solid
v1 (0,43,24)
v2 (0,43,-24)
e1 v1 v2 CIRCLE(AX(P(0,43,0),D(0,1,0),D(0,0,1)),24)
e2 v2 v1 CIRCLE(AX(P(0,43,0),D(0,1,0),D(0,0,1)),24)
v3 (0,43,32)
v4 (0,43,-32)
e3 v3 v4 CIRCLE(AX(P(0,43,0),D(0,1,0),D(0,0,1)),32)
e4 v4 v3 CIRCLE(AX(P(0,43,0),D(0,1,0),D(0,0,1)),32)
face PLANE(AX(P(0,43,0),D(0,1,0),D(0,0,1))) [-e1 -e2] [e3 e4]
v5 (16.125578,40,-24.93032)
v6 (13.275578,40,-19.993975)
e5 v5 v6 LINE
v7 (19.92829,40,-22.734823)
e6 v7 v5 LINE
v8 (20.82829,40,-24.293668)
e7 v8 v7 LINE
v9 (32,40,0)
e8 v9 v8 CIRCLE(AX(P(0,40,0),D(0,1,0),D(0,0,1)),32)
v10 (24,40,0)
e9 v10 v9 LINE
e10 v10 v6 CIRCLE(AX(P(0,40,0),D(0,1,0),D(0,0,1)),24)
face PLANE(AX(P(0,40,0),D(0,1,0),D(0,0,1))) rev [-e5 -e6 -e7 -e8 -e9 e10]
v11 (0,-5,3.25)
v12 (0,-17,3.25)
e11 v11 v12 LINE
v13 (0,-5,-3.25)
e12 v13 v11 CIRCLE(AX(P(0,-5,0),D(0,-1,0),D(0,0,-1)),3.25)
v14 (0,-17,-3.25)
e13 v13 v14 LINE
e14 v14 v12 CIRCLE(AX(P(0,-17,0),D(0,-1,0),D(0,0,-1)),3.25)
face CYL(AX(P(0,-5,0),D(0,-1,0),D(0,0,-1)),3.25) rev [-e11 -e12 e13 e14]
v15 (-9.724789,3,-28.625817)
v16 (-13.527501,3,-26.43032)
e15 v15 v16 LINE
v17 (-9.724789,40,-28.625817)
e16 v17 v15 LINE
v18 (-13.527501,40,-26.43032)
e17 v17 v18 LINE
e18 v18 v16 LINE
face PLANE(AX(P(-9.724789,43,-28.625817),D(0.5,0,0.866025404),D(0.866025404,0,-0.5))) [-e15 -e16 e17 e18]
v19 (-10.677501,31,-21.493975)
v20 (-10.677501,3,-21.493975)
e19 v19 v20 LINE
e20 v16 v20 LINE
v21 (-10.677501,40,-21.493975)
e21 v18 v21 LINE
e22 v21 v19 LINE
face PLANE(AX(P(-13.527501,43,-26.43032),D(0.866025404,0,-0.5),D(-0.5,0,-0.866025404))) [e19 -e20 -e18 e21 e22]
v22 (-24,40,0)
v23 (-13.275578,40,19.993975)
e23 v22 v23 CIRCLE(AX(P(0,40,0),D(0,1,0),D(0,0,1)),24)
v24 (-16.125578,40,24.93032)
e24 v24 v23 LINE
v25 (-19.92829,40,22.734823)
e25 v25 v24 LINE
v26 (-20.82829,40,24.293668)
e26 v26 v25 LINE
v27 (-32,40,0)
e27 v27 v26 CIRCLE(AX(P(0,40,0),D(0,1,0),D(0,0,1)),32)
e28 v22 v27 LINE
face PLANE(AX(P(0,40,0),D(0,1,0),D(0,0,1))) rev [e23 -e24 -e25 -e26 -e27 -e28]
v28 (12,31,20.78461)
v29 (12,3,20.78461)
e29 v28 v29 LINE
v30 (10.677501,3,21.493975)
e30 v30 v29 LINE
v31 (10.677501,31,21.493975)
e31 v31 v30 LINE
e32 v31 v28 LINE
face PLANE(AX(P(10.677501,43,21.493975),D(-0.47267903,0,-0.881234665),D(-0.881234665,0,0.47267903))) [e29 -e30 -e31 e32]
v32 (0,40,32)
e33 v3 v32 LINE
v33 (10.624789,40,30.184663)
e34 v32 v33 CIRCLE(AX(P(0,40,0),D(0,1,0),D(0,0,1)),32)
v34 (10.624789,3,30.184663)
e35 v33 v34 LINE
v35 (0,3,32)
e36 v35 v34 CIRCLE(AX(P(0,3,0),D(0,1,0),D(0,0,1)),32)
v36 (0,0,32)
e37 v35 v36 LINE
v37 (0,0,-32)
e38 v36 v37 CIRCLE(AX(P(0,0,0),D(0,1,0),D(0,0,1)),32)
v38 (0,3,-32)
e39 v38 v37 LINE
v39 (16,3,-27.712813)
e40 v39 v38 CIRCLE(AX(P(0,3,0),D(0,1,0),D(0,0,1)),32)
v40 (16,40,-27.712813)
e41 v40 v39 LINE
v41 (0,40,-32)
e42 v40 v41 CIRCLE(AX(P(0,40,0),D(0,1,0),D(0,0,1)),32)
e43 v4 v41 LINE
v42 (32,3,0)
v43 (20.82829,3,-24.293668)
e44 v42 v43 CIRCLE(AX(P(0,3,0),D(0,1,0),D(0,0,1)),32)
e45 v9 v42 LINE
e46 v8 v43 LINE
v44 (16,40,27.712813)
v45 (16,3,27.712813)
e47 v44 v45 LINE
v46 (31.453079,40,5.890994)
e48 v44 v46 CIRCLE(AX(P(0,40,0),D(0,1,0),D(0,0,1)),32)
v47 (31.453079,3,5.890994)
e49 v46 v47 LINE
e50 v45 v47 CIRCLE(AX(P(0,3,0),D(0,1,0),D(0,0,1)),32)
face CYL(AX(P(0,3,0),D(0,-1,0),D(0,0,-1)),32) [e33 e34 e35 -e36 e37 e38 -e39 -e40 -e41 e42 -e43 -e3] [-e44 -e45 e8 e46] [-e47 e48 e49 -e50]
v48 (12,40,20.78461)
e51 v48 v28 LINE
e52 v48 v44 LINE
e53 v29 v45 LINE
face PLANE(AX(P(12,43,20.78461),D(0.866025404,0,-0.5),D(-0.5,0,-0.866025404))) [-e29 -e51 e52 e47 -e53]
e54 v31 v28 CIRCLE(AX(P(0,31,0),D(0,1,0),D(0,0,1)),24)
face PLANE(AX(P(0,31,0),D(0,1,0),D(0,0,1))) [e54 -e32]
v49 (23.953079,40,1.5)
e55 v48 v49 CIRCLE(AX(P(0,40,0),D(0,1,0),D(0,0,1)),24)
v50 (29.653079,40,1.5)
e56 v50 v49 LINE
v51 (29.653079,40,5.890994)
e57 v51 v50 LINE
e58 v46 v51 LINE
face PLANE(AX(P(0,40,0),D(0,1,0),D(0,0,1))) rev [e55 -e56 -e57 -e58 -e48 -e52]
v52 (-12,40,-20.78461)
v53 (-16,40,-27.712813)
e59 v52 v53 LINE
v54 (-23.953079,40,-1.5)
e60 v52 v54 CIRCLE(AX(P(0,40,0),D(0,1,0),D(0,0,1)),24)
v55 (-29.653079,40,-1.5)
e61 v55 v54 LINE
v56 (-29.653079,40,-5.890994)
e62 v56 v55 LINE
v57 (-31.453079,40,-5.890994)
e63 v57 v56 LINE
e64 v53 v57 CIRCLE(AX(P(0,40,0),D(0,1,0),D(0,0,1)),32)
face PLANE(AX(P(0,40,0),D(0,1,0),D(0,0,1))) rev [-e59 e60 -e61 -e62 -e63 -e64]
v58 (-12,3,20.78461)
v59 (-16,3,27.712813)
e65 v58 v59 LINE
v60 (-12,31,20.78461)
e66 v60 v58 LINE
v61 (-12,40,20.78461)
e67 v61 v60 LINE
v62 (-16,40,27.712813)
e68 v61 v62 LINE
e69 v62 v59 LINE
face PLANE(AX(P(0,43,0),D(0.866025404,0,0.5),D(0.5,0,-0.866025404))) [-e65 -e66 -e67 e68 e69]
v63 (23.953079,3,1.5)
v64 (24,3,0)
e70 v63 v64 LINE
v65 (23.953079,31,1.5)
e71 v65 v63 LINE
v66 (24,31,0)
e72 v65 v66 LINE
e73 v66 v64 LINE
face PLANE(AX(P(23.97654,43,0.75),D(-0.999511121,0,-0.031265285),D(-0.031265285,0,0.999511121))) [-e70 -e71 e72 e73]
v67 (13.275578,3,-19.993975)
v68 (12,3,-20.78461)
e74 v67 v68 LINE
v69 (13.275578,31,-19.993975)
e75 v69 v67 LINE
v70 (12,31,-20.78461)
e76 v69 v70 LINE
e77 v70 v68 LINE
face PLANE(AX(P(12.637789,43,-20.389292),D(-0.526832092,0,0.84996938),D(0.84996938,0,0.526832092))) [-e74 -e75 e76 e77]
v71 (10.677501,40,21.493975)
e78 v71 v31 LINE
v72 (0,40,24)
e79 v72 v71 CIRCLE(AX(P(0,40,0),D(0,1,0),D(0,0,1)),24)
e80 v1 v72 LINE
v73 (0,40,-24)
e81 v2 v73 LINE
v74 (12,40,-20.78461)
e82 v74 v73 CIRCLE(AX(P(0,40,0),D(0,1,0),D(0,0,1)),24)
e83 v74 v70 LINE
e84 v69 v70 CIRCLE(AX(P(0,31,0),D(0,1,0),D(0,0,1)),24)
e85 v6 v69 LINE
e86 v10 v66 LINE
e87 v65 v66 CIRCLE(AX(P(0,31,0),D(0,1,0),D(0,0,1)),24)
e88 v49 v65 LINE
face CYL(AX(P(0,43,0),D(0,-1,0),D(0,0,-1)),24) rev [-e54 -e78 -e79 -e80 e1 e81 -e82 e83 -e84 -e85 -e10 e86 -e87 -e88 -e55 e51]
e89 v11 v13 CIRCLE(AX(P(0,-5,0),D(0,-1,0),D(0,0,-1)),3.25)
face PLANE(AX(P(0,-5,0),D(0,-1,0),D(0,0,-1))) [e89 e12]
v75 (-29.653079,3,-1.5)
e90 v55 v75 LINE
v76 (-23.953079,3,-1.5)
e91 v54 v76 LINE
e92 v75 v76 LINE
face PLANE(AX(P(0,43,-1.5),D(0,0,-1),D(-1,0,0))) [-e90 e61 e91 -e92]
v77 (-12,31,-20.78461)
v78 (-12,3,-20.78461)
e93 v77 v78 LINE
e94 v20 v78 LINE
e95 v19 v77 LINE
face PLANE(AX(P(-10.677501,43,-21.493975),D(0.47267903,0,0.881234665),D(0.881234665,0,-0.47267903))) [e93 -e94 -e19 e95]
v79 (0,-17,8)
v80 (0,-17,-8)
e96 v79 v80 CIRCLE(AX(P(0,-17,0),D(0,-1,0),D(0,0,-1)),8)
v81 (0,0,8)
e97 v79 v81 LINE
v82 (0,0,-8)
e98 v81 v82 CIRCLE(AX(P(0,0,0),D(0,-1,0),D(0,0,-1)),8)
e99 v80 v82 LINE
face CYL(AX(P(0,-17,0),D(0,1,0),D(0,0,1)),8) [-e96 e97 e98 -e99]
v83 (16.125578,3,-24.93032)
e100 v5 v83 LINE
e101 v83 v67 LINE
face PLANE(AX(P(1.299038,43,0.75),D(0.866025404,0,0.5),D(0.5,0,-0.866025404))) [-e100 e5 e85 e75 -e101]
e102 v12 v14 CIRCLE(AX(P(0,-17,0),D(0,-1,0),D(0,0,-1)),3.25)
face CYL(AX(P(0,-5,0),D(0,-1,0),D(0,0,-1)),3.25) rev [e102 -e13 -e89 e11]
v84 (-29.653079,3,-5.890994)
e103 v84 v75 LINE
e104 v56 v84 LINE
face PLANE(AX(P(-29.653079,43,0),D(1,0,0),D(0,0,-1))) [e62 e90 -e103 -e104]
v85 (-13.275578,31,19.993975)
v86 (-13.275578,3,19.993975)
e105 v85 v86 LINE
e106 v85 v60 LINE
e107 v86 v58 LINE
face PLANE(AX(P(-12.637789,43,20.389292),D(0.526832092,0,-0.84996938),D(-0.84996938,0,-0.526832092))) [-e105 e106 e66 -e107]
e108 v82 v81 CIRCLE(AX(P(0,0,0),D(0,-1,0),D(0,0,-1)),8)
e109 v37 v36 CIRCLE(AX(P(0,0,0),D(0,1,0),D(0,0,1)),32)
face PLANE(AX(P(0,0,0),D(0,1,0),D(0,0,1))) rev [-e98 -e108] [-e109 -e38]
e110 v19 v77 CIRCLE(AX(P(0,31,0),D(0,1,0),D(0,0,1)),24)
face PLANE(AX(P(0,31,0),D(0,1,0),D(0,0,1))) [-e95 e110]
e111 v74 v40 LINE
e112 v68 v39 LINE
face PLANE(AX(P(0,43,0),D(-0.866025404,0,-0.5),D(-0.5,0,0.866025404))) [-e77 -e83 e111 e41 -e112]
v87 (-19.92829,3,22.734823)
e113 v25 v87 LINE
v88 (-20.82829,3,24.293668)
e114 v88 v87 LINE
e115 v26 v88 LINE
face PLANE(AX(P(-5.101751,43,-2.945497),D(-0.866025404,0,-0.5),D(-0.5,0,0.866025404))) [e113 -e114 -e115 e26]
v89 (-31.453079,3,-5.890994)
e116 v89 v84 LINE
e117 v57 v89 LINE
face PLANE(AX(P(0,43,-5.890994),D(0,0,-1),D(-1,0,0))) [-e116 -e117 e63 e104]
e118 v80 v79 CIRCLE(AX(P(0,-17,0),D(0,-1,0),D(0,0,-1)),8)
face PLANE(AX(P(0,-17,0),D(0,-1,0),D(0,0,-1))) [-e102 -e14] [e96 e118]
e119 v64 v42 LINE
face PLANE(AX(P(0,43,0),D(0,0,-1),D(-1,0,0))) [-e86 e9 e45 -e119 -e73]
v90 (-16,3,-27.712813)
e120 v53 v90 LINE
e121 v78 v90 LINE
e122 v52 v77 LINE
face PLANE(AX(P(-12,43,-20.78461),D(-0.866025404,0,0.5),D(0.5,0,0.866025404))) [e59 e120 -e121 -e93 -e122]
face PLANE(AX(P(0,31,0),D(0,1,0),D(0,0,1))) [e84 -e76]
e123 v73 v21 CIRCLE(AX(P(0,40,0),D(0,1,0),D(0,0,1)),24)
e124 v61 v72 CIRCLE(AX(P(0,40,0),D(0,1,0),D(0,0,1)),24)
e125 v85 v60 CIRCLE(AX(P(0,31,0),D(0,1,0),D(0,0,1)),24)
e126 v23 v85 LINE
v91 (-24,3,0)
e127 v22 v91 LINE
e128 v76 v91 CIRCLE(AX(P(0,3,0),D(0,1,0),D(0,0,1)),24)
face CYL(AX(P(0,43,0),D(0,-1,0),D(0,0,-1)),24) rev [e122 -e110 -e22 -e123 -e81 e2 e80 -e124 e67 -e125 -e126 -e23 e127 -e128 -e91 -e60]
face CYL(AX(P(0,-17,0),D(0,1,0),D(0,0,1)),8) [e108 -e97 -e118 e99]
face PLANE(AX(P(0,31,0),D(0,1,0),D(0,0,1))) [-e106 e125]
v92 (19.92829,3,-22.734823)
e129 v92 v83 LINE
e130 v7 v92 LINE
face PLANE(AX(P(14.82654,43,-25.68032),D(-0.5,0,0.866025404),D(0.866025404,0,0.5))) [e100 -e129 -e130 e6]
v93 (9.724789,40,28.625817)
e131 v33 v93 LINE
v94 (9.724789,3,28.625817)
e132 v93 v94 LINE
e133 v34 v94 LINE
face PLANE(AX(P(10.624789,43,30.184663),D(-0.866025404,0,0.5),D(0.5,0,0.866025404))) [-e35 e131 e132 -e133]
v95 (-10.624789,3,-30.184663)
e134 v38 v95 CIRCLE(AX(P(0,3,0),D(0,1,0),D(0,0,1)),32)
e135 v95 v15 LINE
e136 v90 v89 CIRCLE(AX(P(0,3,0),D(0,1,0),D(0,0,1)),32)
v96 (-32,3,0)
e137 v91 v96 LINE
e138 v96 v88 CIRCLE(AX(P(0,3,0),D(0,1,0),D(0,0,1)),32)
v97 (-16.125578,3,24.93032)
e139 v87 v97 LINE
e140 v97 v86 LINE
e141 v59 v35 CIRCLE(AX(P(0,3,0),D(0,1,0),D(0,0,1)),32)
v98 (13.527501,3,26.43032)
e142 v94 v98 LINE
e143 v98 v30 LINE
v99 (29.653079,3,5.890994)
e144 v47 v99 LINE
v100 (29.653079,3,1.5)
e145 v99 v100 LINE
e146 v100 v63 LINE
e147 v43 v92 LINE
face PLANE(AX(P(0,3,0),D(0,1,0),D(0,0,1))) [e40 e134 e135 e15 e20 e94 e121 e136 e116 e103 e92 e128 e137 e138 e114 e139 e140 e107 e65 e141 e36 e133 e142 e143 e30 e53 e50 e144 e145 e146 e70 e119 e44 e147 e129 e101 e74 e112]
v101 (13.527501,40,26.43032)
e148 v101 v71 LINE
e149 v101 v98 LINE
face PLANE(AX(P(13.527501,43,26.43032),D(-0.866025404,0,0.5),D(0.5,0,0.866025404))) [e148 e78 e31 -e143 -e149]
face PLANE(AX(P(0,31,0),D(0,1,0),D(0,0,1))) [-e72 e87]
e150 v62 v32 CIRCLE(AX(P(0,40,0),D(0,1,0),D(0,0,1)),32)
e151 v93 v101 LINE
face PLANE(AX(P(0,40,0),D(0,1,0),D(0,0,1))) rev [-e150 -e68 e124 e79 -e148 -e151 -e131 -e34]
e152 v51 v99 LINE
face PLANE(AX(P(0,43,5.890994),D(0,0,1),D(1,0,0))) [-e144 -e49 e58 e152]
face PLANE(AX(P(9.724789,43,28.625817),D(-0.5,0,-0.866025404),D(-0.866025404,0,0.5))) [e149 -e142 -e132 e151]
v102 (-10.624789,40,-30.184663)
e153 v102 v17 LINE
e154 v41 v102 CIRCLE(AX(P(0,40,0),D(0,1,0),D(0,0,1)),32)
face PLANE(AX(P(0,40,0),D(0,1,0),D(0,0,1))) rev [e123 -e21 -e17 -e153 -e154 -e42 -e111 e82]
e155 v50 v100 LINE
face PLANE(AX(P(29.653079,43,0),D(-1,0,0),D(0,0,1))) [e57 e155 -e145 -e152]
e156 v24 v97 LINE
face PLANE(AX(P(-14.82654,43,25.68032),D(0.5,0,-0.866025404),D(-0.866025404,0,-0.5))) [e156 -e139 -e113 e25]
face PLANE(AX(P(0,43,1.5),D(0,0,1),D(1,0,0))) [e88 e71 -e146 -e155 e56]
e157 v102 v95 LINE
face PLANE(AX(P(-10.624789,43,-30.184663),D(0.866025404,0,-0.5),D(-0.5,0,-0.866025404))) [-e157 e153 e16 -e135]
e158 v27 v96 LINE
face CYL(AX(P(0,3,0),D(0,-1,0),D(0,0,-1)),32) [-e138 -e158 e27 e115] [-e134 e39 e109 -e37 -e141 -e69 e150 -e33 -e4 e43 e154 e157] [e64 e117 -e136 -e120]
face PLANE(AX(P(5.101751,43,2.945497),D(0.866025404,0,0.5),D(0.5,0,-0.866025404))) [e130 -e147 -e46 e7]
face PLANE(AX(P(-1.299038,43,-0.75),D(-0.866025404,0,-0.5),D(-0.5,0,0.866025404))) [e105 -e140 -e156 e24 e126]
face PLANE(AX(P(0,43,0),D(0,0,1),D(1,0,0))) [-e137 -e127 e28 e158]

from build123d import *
from build123d.topology import SkipClean

# Parameters (mm, degrees)
BASE_DISC_SKETCH_R    = 32
BASE_DISC_64_DEPTH    = 3
CAGE_POSTS_6X_DEPTH   = 40
TOP_START             = -3
TOP_RING_SKETCH_R     = 32
TOP_RING_DEPTH        = 3
HUB_SKETCH_R          = 8
HUB_16_DEPTH          = 17
HUB_BORE_SKETCH_R     = 3.25
HUB_BORE_6_5_DEPTH    = 12
INNER_START           = -12
INNER_RECESS_SKETCH_R = 24
INNER_RECESS_48_DEPTH = 12


with BuildPart() as part:
    # Base Disc Sketch → Base Disc Ø64 (new body)
    with BuildSketch(Plane(origin=(0, 0, 0), x_dir=(1, 0, 0), z_dir=(0, 1, 0))):
        with Locations(Location((0, 0, 0), (0, 0, 270))):
            Circle(BASE_DISC_SKETCH_R)
    extrude(amount=BASE_DISC_64_DEPTH)

    # Cage Posts Sketch → Cage Posts 6x (add)
    with SkipClean():  # the faces are left unmerged after this step: merging them gives an invalid solid
        with BuildSketch(Plane(origin=(0, 3, 0), x_dir=(1, 0, 0), z_dir=(0, 1, 0))):
            with BuildLine():
                Line((-19.928290222, -22.734822717), (-20.828290222, -24.293668443))
                ThreePointArc((-20.828290222, -24.293668443), (-18.493333323, -26.115065051), (-16, -27.712812921))
                Line((-16, -27.712812921), (-12, -20.784609691))
                Line((-12, -20.784609691), (-13.275577673, -19.993975029))
                Line((-13.275577673, -19.993975029), (-16.125577673, -24.93031983))
                Line((-16.125577673, -24.93031983), (-19.928290222, -22.734822717))
            make_face()
            with BuildLine():
                Line((29.653079134, -5.890994228), (31.453079134, -5.890994228))
                ThreePointArc((31.453079134, -5.890994228), (31.862976417, -2.958163933), (32, 0))
                Line((32, 0), (24, 0))
                Line((24, 0), (23.953079134, -1.5))
                Line((23.953079134, -1.5), (29.653079134, -1.5))
                Line((29.653079134, -1.5), (29.653079134, -5.890994228))
            make_face()
            with BuildLine():
                ThreePointArc((20.828290222, 24.293668443), (18.493333323, 26.115065051), (16, 27.712812921))
                Line((16, 27.712812921), (12, 20.784609691))
                Line((12, 20.784609691), (13.275577673, 19.993975029))
                Line((13.275577673, 19.993975029), (16.125577673, 24.93031983))
                Line((16.125577673, 24.93031983), (19.928290222, 22.734822717))
                Line((19.928290222, 22.734822717), (20.828290222, 24.293668443))
            make_face()
            with BuildLine():
                Line((-32, 0), (-24, 0))
                ThreePointArc((-24, 0), (-23.988266915, 0.750366838), (-23.953079134, 1.5))
                Line((-23.953079134, 1.5), (-29.653079134, 1.5))
                Line((-29.653079134, 1.5), (-29.653079134, 5.890994228))
                Line((-29.653079134, 5.890994228), (-31.453079134, 5.890994228))
                ThreePointArc((-31.453079134, 5.890994228), (-31.862976417, 2.958163933), (-32, 0))
            make_face()
            with BuildLine():
                Line((9.724788912, -28.625816944), (13.527501461, -26.43031983))
                Line((13.527501461, -26.43031983), (10.677501461, -21.493975029))
                Line((10.677501461, -21.493975029), (12, -20.784609691))
                Line((12, -20.784609691), (16, -27.712812921))
                ThreePointArc((16, -27.712812921), (13.369643094, -29.073228984), (10.624788912, -30.184662671))
                Line((10.624788912, -30.184662671), (9.724788912, -28.625816944))
            make_face()
            with BuildLine():
                ThreePointArc((-16, 27.712812921), (-13.369643094, 29.073228984), (-10.624788912, 30.184662671))
                Line((-10.624788912, 30.184662671), (-9.724788912, 28.625816944))
                Line((-9.724788912, 28.625816944), (-13.527501461, 26.43031983))
                Line((-13.527501461, 26.43031983), (-10.677501461, 21.493975029))
                Line((-10.677501461, 21.493975029), (-12, 20.784609691))
                Line((-12, 20.784609691), (-16, 27.712812921))
            make_face()
        extrude(amount=CAGE_POSTS_6X_DEPTH)

    # Top Ring Sketch → Top Ring (add)
    with SkipClean():  # the faces are left unmerged after this step: merging them gives an invalid solid
        with BuildSketch(Plane(origin=(0, 43, 0), x_dir=(1, 0, 0), z_dir=(0, 1, 0)).offset(TOP_START)):
            with Locations(Location((0, 0, 0), (0, 0, 270))):
                Circle(TOP_RING_SKETCH_R)
        extrude(amount=TOP_RING_DEPTH)

    # Hub Sketch → Hub Ø16 (add)
    with SkipClean():  # the faces are left unmerged after this step: merging them gives an invalid solid
        with BuildSketch(Plane.XZ):
            with Locations(Location((0, 0, 0), (0, 0, 270))):
                Circle(HUB_SKETCH_R)
        extrude(amount=HUB_16_DEPTH)

    # Hub Bore Sketch → Hub Bore Ø6.5 (cut)
    with SkipClean():  # the faces are left unmerged after this step: merging them gives an invalid solid
        with BuildSketch(Plane.XZ.offset(17)):
            with Locations(Location((0, 0, 0), (0, 0, 270))):
                Circle(HUB_BORE_SKETCH_R)
        extrude(amount=-HUB_BORE_6_5_DEPTH, mode=Mode.SUBTRACT)

    # Inner Recess Sketch → Inner Recess Ø48 (cut)
    with SkipClean():  # the faces are left unmerged after this step: merging them gives an invalid solid
        with BuildSketch(Plane(origin=(0, 43, 0), x_dir=(1, 0, 0), z_dir=(0, 1, 0)).offset(INNER_START)):
            with Locations(Location((0, 0, 0), (0, 0, 116.416678302))):
                Circle(INNER_RECESS_SKETCH_R)
        extrude(amount=INNER_RECESS_48_DEPTH, mode=Mode.SUBTRACT)


solid = part.part
